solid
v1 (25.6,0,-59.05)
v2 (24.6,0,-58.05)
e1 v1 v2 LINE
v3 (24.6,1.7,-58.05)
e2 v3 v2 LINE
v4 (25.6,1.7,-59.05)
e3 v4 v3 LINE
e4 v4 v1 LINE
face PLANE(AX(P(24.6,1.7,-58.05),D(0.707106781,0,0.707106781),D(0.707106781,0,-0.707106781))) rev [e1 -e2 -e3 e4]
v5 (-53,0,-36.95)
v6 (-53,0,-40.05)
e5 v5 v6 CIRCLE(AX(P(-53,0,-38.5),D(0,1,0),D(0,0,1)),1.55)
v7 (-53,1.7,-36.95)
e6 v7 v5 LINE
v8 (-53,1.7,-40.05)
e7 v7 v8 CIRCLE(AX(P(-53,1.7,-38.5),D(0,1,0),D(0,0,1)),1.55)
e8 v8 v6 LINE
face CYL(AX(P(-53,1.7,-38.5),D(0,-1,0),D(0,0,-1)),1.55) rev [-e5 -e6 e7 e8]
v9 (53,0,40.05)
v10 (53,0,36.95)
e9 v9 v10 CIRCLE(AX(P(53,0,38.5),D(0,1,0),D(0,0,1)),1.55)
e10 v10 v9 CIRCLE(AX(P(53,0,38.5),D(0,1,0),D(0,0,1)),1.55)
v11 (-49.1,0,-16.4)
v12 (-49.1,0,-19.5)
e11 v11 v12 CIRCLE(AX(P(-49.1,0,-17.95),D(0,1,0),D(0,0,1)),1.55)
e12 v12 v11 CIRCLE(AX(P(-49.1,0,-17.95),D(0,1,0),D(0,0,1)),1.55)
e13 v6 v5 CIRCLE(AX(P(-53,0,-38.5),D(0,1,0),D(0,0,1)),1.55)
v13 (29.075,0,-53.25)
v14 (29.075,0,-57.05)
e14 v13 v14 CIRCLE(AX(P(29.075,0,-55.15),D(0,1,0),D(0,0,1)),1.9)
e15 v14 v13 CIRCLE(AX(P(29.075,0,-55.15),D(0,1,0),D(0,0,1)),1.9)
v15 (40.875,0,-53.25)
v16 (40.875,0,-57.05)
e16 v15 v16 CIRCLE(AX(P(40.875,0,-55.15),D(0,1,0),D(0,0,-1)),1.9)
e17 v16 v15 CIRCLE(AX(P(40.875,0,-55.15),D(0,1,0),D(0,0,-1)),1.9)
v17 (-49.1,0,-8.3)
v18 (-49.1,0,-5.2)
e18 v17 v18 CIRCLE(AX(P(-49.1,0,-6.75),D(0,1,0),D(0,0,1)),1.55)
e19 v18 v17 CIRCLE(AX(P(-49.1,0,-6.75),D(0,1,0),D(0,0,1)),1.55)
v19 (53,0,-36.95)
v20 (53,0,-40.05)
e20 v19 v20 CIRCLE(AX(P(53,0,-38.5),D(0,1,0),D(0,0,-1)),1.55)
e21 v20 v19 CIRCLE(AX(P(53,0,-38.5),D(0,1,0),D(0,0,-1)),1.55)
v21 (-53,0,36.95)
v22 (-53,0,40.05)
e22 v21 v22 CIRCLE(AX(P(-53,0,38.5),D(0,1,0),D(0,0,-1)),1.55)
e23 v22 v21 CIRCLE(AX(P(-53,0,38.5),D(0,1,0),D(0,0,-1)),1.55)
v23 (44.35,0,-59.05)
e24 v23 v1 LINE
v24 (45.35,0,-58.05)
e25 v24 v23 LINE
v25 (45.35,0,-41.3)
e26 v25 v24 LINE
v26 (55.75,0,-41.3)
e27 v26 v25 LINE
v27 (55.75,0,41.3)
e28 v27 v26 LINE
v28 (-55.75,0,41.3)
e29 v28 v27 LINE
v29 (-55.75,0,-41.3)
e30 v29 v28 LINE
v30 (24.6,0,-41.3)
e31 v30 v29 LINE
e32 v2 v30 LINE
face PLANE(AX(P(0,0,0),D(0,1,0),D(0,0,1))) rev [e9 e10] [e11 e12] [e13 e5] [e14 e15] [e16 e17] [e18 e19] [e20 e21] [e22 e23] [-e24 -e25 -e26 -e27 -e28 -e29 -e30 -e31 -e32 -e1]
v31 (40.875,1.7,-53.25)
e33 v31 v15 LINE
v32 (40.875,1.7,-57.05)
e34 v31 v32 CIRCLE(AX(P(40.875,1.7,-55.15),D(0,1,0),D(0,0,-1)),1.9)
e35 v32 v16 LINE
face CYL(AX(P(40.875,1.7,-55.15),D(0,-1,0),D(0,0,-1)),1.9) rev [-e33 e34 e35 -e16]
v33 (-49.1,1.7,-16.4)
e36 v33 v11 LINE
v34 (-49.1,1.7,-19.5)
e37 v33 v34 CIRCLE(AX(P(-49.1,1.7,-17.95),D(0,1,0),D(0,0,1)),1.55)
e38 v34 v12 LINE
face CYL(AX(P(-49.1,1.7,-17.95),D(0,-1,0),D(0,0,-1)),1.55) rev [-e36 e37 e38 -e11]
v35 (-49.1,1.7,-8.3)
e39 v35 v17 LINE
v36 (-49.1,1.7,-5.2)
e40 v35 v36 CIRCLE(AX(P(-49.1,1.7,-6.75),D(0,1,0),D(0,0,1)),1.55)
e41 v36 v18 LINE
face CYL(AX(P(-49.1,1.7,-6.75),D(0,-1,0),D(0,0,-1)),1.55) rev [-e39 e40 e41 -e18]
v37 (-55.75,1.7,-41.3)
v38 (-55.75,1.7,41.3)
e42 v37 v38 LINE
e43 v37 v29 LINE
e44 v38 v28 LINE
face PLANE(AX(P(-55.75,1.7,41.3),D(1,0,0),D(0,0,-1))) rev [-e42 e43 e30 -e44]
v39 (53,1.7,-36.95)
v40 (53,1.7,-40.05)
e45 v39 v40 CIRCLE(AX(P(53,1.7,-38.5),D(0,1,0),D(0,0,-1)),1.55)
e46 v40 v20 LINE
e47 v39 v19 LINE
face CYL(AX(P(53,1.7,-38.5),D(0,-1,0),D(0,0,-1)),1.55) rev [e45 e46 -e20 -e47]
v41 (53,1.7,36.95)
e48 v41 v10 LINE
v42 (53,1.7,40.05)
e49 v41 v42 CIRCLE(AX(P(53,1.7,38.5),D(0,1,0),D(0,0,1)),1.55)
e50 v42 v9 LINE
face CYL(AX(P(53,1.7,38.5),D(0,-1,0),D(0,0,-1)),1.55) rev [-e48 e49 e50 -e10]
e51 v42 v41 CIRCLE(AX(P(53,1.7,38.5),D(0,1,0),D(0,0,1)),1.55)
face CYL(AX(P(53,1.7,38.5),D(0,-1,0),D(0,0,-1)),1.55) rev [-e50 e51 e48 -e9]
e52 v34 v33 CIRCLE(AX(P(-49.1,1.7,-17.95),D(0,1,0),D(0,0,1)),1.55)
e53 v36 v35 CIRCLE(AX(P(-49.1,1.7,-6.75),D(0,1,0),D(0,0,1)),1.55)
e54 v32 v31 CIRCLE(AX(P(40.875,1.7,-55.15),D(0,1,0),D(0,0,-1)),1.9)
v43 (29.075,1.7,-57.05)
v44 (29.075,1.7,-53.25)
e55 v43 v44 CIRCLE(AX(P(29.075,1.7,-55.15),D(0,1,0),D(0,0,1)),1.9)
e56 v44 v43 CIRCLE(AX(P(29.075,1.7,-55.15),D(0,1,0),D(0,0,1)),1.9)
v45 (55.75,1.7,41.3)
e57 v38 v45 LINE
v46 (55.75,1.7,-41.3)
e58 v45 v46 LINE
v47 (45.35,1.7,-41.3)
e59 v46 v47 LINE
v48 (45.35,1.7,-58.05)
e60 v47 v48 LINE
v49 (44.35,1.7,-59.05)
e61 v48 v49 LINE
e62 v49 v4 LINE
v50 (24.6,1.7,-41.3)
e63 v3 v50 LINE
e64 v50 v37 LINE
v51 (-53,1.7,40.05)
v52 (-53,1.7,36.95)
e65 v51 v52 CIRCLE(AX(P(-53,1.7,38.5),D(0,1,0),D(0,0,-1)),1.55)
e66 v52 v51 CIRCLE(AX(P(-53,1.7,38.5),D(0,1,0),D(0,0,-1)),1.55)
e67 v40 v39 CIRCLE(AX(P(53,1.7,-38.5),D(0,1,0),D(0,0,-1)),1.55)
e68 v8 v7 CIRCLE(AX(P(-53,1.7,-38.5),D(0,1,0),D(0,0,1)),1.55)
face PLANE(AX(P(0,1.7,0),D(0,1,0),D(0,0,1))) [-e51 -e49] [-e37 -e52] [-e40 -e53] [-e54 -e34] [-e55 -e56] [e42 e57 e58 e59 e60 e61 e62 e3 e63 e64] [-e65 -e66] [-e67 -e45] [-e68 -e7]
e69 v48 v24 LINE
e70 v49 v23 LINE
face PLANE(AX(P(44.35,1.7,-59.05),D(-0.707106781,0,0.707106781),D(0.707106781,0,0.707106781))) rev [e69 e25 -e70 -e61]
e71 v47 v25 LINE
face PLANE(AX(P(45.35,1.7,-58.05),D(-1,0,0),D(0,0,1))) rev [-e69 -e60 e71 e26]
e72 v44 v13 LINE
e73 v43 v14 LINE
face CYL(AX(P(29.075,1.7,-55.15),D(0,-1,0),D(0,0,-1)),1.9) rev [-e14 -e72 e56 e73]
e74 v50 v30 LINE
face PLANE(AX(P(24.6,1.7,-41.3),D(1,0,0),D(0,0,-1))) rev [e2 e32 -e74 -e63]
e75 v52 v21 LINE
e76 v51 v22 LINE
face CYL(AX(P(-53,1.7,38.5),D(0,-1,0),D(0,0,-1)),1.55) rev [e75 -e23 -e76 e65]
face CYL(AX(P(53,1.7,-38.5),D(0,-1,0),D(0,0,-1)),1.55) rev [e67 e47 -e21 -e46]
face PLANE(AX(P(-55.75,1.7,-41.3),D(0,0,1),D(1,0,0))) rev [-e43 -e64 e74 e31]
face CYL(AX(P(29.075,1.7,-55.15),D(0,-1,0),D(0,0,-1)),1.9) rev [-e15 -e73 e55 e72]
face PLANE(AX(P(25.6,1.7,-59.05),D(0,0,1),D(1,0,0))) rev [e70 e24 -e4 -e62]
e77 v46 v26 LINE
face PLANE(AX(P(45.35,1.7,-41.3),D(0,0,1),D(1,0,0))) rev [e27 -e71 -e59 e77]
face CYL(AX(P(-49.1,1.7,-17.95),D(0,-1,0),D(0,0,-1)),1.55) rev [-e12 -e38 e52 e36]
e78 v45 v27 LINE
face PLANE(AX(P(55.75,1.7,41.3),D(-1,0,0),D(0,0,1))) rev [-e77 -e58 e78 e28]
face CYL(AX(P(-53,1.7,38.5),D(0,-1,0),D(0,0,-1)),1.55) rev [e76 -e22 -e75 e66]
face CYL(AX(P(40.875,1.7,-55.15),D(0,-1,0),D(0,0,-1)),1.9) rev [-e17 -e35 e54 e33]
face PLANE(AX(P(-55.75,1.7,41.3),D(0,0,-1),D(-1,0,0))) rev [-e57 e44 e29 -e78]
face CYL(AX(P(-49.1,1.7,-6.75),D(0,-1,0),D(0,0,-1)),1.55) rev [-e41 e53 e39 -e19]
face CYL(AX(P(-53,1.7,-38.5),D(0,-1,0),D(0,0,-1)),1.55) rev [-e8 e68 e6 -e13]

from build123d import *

# Parameters (mm, degrees)
SKETCH_1_R      = 1.55
SKETCH_1_R_2    = 1.9
EXTRUDE_1_DEPTH = 1.7


with BuildPart() as part:
    # 草图1 → 凸台-拉伸1 (new body)
    with BuildSketch(Plane(origin=(0, 0, 0), x_dir=(1, 0, 0), z_dir=(0, 1, 0))):
        Polygon((-55.75, -41.3), (55.75, -41.3), (55.75, 41.3), (45.35, 41.3), (45.35, 58.05), (44.35, 59.05), (25.6, 59.05), (24.6, 58.05), (24.6, 41.3), (-55.75, 41.3), align=None)
        with Locations(Location((-53, 38.5, 0), (0, 0, 270))):
            Circle(SKETCH_1_R, mode=Mode.SUBTRACT)
        with Locations(Location((53, 38.5, 0), (0, 0, 90))):
            Circle(SKETCH_1_R, mode=Mode.SUBTRACT)
        with Locations(Location((53, -38.5, 0), (0, 0, 270))):
            Circle(SKETCH_1_R, mode=Mode.SUBTRACT)
        with Locations(Location((-53, -38.5, 0), (0, 0, 90))):
            Circle(SKETCH_1_R, mode=Mode.SUBTRACT)
        with Locations(Location((29.075, 55.15, 0), (0, 0, 270))):
            Circle(SKETCH_1_R_2, mode=Mode.SUBTRACT)
        with Locations(Location((40.875, 55.15, 0), (0, 0, 90))):
            Circle(SKETCH_1_R_2, mode=Mode.SUBTRACT)
        with Locations(Location((-49.1, 17.95, 0), (0, 0, 270))):
            Circle(SKETCH_1_R, mode=Mode.SUBTRACT)
        with Locations(Location((-49.1, 6.75, 0), (0, 0, 270))):
            Circle(SKETCH_1_R, mode=Mode.SUBTRACT)
    extrude(amount=EXTRUDE_1_DEPTH)


solid = part.part
